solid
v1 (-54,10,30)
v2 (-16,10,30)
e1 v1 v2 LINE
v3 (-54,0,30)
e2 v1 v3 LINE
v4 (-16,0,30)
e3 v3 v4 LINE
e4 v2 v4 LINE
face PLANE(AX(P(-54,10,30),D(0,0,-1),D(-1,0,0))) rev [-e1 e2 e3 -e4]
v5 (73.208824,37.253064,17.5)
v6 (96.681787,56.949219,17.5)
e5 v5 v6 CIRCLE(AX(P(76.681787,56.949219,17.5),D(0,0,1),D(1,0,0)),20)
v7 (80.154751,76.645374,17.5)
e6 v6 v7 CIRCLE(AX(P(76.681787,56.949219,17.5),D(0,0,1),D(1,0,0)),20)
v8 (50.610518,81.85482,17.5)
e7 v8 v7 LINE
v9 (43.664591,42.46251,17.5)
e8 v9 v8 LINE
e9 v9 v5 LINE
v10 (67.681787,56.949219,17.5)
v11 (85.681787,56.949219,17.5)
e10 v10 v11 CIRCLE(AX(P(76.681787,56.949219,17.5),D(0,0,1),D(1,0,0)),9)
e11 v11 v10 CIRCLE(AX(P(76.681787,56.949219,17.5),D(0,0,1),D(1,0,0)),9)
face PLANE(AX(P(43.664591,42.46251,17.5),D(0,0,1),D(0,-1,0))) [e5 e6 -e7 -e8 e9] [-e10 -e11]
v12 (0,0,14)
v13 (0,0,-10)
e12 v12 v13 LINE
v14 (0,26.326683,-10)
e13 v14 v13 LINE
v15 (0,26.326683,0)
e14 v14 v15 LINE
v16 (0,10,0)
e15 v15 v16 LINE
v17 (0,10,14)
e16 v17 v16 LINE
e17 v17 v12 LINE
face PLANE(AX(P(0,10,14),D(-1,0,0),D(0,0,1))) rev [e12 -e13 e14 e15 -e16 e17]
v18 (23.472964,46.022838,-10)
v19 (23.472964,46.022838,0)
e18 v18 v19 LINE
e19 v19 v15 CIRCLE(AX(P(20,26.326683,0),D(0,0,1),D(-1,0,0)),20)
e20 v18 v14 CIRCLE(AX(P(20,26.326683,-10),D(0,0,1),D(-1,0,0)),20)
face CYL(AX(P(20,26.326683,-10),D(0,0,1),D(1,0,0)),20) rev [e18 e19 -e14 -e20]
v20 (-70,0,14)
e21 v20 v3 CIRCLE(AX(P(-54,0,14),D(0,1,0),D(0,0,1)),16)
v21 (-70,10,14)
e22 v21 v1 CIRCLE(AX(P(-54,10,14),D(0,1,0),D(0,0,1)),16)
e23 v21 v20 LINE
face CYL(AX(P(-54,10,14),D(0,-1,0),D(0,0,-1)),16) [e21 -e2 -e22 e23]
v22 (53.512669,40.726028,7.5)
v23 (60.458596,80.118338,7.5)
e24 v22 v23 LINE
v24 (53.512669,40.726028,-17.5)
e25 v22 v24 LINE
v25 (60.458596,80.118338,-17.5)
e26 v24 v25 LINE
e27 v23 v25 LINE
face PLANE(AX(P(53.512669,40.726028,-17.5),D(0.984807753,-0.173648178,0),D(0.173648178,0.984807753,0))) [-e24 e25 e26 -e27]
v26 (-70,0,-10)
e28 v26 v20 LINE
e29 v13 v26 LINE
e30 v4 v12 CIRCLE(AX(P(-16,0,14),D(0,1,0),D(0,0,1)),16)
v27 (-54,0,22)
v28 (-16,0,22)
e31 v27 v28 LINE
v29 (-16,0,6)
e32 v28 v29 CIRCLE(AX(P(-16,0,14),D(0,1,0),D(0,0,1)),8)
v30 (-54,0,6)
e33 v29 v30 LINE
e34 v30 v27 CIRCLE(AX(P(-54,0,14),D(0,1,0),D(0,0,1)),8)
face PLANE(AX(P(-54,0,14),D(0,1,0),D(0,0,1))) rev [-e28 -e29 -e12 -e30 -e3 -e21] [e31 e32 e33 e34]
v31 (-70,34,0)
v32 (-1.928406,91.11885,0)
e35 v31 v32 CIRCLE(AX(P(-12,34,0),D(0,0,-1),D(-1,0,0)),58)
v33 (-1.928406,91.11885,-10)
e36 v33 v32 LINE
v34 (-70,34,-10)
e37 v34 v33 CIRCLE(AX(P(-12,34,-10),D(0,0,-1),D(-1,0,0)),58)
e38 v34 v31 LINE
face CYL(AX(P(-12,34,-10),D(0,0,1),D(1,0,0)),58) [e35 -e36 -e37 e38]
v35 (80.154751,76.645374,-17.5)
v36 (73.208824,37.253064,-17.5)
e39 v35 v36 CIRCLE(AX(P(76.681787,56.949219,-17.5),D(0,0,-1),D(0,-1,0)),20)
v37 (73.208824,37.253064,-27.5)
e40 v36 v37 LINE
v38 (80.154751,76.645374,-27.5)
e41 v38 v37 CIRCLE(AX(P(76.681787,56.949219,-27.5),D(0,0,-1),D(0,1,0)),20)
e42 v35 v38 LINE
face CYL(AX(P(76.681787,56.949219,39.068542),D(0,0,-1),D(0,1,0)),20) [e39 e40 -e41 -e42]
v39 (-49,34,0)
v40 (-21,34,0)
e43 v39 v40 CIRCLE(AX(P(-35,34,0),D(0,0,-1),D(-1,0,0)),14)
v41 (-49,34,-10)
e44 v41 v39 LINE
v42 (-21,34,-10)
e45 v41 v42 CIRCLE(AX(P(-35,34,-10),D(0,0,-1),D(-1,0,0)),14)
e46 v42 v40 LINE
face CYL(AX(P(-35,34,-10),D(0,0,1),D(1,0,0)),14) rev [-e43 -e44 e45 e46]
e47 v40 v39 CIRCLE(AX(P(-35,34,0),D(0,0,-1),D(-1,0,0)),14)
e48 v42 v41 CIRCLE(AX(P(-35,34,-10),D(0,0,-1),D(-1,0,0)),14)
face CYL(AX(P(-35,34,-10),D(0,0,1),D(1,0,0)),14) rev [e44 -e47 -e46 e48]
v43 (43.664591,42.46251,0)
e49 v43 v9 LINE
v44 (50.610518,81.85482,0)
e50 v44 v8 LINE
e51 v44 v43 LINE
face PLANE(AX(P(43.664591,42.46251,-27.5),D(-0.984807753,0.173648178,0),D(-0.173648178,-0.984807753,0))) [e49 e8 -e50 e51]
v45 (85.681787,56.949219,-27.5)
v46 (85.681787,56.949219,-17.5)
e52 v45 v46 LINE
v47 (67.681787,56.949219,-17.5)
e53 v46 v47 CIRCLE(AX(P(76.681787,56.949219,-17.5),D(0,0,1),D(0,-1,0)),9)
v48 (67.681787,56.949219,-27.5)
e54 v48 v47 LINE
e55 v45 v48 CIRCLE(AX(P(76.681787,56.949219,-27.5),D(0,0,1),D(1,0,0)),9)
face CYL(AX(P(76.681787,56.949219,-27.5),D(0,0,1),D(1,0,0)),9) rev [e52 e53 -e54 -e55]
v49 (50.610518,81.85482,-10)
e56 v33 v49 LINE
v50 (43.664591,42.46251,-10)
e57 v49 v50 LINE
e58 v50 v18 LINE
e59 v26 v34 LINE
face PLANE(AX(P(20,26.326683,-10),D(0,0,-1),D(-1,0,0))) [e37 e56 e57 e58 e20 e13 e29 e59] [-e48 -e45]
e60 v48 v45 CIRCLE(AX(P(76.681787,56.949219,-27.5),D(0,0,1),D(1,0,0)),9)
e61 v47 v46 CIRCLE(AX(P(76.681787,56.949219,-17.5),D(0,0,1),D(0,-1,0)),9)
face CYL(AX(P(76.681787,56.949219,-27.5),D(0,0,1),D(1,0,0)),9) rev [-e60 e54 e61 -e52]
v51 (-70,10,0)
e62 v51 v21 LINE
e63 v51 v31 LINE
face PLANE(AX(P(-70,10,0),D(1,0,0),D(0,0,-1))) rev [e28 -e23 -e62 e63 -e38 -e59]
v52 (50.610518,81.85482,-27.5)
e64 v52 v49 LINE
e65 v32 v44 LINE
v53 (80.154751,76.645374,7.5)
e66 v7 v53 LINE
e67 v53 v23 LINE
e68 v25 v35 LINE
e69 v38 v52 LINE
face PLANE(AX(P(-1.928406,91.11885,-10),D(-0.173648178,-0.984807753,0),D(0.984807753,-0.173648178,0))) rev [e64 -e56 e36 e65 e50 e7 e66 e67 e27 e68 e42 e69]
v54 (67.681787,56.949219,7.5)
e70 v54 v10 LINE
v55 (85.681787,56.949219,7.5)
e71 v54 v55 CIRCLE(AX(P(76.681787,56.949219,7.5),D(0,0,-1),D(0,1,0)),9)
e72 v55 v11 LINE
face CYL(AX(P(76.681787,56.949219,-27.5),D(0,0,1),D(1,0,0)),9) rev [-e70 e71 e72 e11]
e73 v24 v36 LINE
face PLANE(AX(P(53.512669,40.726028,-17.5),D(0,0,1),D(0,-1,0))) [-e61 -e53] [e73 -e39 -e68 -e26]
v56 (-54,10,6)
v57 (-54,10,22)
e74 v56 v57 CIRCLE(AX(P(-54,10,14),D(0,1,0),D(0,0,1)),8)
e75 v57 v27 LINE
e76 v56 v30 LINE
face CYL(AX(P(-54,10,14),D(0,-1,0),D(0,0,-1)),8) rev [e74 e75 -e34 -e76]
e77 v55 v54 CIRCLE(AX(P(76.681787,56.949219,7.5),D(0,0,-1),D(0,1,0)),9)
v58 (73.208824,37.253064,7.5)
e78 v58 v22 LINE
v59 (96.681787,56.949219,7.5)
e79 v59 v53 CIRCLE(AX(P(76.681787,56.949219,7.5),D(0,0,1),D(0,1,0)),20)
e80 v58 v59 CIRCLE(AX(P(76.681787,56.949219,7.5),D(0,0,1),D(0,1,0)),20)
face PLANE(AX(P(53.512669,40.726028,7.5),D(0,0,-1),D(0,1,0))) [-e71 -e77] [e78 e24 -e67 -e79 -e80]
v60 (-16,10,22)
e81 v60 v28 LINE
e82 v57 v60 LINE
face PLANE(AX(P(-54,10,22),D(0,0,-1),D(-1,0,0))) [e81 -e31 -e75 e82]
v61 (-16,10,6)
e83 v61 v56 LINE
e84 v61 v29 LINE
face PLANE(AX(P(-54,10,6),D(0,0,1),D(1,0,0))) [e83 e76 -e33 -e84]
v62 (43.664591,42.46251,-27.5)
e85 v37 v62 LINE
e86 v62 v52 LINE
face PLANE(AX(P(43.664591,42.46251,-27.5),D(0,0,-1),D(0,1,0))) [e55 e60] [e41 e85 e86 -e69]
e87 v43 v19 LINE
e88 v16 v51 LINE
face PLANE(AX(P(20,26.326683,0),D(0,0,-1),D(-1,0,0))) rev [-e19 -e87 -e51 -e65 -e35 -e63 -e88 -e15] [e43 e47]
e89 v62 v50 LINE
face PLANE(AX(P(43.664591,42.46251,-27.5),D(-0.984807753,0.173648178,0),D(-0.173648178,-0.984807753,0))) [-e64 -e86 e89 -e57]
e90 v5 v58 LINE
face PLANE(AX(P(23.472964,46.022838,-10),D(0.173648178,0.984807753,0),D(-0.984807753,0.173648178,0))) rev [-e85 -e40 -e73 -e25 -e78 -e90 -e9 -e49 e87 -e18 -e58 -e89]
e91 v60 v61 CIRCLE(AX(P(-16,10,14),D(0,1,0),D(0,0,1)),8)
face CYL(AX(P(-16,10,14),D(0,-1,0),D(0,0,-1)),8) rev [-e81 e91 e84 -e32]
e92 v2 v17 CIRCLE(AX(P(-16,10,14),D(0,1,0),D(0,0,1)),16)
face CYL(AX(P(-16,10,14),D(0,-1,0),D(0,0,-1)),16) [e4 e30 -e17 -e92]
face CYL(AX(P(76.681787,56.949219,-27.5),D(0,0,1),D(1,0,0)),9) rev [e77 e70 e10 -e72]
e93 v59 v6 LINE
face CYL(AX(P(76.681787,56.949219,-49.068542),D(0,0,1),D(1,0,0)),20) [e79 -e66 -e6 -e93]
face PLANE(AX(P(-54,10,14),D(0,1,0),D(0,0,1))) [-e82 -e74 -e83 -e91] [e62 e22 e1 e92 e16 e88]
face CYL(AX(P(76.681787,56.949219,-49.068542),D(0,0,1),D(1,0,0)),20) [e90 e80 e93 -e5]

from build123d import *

# Parameters (mm, degrees)
SLOTTED_BASE_PLATE_DEPTH = 10
UPRIGHT_WEB_SKETCH_R     = 14
UPRIGHT_WEB_DEPTH        = 10
CLEVIS_ARM_DEPTH         = 40
CLEVIS_EAR_1_SKETCH_R    = 20
CLEVIS_EAR_1_DEPTH       = 10
CLEVIS_START             = -10
CLEVIS_EAR_2_SKETCH_R    = 20
CLEVIS_EAR_2_DEPTH       = 10
CLEVIS_PIN_HOLE_SKETCH_R = 9
CLEVIS_PIN_HOLE_18_DEPTH = 141.841641644


with BuildPart() as part:
    # Base Plate Sketch → Slotted Base Plate (new body)
    with BuildSketch(Plane(origin=(0, 0, 0), x_dir=(1, 0, 0), z_dir=(0, 1, 0))):
        with BuildLine():
            Line((0, 0), (-70, 0))
            Line((-70, 0), (-70, -14))
            ThreePointArc((-70, -14), (-65.313708499, -25.313708499), (-54, -30))
            Line((-54, -30), (-16, -30))
            ThreePointArc((-16, -30), (-4.686291501, -25.313708499), (0, -14))
            Line((0, -14), (0, 0))
        make_face()
        with BuildLine():
            Line((-54, -6), (-16, -6))
            ThreePointArc((-16, -6), (-8, -14), (-16, -22))
            Line((-16, -22), (-54, -22))
            ThreePointArc((-54, -22), (-62, -14), (-54, -6))
        make_face(mode=Mode.SUBTRACT)
    extrude(amount=SLOTTED_BASE_PLATE_DEPTH)

    # Upright Web Sketch → Upright Web (add)
    with BuildSketch(Plane(origin=(0, 0, 0), x_dir=(-1, 0, 0), z_dir=(0, 0, -1))):
        with BuildLine():
            Line((70, 0), (70, 34))
            ThreePointArc((70, 34), (49.281681362, 78.430577701), (1.928405695, 91.118849675))
            Line((1.928405695, 91.118849675), (-50.610518395, 81.85481982))
            Line((-50.610518395, 81.85481982), (-43.664591288, 42.4625097))
            Line((-43.664591288, 42.4625097), (-23.472963553, 46.022838454))
            ThreePointArc((-23.472963553, 46.022838454), (-7.144247806, 41.647572256), (0, 26.326683394))
            Line((0, 26.326683394), (0, 0))
            Line((0, 0), (70, 0))
        make_face()
        with Locations((35, 34)):
            Circle(UPRIGHT_WEB_SKETCH_R, mode=Mode.SUBTRACT)
    extrude(amount=UPRIGHT_WEB_DEPTH)

    # Clevis Arm Sketch → Clevis Arm (add)
    with BuildSketch(Plane(origin=(15.524092466, 88.041503368, 0), x_dir=(0.9848077530122072, -0.17364817766693494, 0), z_dir=(0.17364817766693494, 0.9848077530122072, 0))):
        Polygon((35.627690604, 27.5), (45.627690604, 27.5), (65.627690604, 27.5), (65.627690604, 17.5), (45.627690604, 17.5), (45.627690604, -7.5), (65.627690604, -7.5), (65.627690604, -17.5), (35.627690604, -17.5), align=None)
    extrude(amount=-CLEVIS_ARM_DEPTH)

    # Clevis Ear 1 Sketch → Clevis Ear 1 (add)
    with BuildSketch(Plane.XY.offset(17.5)):
        with Locations((76.681787432, 56.94921943)):
            Circle(CLEVIS_EAR_1_SKETCH_R)
    extrude(amount=-CLEVIS_EAR_1_DEPTH)

    # Clevis Ear 2 Sketch → Clevis Ear 2 (add)
    with BuildSketch(Plane(origin=(0, 0, -27.5), x_dir=(-1, 0, 0), z_dir=(0, 0, -1)).offset(CLEVIS_START)):
        with Locations((-76.681787432, 56.94921943)):
            Circle(CLEVIS_EAR_2_SKETCH_R)
    extrude(amount=CLEVIS_EAR_2_DEPTH)

    # Clevis Pin Hole Sketch → Clevis Pin Hole Ø18 (cut, through all)
    with BuildSketch(Plane.XY.offset(17.5)):
        with Locations((76.681787432, 56.94921943)):
            Circle(CLEVIS_PIN_HOLE_SKETCH_R)
    extrude(amount=-CLEVIS_PIN_HOLE_18_DEPTH, mode=Mode.SUBTRACT)


solid = part.part
